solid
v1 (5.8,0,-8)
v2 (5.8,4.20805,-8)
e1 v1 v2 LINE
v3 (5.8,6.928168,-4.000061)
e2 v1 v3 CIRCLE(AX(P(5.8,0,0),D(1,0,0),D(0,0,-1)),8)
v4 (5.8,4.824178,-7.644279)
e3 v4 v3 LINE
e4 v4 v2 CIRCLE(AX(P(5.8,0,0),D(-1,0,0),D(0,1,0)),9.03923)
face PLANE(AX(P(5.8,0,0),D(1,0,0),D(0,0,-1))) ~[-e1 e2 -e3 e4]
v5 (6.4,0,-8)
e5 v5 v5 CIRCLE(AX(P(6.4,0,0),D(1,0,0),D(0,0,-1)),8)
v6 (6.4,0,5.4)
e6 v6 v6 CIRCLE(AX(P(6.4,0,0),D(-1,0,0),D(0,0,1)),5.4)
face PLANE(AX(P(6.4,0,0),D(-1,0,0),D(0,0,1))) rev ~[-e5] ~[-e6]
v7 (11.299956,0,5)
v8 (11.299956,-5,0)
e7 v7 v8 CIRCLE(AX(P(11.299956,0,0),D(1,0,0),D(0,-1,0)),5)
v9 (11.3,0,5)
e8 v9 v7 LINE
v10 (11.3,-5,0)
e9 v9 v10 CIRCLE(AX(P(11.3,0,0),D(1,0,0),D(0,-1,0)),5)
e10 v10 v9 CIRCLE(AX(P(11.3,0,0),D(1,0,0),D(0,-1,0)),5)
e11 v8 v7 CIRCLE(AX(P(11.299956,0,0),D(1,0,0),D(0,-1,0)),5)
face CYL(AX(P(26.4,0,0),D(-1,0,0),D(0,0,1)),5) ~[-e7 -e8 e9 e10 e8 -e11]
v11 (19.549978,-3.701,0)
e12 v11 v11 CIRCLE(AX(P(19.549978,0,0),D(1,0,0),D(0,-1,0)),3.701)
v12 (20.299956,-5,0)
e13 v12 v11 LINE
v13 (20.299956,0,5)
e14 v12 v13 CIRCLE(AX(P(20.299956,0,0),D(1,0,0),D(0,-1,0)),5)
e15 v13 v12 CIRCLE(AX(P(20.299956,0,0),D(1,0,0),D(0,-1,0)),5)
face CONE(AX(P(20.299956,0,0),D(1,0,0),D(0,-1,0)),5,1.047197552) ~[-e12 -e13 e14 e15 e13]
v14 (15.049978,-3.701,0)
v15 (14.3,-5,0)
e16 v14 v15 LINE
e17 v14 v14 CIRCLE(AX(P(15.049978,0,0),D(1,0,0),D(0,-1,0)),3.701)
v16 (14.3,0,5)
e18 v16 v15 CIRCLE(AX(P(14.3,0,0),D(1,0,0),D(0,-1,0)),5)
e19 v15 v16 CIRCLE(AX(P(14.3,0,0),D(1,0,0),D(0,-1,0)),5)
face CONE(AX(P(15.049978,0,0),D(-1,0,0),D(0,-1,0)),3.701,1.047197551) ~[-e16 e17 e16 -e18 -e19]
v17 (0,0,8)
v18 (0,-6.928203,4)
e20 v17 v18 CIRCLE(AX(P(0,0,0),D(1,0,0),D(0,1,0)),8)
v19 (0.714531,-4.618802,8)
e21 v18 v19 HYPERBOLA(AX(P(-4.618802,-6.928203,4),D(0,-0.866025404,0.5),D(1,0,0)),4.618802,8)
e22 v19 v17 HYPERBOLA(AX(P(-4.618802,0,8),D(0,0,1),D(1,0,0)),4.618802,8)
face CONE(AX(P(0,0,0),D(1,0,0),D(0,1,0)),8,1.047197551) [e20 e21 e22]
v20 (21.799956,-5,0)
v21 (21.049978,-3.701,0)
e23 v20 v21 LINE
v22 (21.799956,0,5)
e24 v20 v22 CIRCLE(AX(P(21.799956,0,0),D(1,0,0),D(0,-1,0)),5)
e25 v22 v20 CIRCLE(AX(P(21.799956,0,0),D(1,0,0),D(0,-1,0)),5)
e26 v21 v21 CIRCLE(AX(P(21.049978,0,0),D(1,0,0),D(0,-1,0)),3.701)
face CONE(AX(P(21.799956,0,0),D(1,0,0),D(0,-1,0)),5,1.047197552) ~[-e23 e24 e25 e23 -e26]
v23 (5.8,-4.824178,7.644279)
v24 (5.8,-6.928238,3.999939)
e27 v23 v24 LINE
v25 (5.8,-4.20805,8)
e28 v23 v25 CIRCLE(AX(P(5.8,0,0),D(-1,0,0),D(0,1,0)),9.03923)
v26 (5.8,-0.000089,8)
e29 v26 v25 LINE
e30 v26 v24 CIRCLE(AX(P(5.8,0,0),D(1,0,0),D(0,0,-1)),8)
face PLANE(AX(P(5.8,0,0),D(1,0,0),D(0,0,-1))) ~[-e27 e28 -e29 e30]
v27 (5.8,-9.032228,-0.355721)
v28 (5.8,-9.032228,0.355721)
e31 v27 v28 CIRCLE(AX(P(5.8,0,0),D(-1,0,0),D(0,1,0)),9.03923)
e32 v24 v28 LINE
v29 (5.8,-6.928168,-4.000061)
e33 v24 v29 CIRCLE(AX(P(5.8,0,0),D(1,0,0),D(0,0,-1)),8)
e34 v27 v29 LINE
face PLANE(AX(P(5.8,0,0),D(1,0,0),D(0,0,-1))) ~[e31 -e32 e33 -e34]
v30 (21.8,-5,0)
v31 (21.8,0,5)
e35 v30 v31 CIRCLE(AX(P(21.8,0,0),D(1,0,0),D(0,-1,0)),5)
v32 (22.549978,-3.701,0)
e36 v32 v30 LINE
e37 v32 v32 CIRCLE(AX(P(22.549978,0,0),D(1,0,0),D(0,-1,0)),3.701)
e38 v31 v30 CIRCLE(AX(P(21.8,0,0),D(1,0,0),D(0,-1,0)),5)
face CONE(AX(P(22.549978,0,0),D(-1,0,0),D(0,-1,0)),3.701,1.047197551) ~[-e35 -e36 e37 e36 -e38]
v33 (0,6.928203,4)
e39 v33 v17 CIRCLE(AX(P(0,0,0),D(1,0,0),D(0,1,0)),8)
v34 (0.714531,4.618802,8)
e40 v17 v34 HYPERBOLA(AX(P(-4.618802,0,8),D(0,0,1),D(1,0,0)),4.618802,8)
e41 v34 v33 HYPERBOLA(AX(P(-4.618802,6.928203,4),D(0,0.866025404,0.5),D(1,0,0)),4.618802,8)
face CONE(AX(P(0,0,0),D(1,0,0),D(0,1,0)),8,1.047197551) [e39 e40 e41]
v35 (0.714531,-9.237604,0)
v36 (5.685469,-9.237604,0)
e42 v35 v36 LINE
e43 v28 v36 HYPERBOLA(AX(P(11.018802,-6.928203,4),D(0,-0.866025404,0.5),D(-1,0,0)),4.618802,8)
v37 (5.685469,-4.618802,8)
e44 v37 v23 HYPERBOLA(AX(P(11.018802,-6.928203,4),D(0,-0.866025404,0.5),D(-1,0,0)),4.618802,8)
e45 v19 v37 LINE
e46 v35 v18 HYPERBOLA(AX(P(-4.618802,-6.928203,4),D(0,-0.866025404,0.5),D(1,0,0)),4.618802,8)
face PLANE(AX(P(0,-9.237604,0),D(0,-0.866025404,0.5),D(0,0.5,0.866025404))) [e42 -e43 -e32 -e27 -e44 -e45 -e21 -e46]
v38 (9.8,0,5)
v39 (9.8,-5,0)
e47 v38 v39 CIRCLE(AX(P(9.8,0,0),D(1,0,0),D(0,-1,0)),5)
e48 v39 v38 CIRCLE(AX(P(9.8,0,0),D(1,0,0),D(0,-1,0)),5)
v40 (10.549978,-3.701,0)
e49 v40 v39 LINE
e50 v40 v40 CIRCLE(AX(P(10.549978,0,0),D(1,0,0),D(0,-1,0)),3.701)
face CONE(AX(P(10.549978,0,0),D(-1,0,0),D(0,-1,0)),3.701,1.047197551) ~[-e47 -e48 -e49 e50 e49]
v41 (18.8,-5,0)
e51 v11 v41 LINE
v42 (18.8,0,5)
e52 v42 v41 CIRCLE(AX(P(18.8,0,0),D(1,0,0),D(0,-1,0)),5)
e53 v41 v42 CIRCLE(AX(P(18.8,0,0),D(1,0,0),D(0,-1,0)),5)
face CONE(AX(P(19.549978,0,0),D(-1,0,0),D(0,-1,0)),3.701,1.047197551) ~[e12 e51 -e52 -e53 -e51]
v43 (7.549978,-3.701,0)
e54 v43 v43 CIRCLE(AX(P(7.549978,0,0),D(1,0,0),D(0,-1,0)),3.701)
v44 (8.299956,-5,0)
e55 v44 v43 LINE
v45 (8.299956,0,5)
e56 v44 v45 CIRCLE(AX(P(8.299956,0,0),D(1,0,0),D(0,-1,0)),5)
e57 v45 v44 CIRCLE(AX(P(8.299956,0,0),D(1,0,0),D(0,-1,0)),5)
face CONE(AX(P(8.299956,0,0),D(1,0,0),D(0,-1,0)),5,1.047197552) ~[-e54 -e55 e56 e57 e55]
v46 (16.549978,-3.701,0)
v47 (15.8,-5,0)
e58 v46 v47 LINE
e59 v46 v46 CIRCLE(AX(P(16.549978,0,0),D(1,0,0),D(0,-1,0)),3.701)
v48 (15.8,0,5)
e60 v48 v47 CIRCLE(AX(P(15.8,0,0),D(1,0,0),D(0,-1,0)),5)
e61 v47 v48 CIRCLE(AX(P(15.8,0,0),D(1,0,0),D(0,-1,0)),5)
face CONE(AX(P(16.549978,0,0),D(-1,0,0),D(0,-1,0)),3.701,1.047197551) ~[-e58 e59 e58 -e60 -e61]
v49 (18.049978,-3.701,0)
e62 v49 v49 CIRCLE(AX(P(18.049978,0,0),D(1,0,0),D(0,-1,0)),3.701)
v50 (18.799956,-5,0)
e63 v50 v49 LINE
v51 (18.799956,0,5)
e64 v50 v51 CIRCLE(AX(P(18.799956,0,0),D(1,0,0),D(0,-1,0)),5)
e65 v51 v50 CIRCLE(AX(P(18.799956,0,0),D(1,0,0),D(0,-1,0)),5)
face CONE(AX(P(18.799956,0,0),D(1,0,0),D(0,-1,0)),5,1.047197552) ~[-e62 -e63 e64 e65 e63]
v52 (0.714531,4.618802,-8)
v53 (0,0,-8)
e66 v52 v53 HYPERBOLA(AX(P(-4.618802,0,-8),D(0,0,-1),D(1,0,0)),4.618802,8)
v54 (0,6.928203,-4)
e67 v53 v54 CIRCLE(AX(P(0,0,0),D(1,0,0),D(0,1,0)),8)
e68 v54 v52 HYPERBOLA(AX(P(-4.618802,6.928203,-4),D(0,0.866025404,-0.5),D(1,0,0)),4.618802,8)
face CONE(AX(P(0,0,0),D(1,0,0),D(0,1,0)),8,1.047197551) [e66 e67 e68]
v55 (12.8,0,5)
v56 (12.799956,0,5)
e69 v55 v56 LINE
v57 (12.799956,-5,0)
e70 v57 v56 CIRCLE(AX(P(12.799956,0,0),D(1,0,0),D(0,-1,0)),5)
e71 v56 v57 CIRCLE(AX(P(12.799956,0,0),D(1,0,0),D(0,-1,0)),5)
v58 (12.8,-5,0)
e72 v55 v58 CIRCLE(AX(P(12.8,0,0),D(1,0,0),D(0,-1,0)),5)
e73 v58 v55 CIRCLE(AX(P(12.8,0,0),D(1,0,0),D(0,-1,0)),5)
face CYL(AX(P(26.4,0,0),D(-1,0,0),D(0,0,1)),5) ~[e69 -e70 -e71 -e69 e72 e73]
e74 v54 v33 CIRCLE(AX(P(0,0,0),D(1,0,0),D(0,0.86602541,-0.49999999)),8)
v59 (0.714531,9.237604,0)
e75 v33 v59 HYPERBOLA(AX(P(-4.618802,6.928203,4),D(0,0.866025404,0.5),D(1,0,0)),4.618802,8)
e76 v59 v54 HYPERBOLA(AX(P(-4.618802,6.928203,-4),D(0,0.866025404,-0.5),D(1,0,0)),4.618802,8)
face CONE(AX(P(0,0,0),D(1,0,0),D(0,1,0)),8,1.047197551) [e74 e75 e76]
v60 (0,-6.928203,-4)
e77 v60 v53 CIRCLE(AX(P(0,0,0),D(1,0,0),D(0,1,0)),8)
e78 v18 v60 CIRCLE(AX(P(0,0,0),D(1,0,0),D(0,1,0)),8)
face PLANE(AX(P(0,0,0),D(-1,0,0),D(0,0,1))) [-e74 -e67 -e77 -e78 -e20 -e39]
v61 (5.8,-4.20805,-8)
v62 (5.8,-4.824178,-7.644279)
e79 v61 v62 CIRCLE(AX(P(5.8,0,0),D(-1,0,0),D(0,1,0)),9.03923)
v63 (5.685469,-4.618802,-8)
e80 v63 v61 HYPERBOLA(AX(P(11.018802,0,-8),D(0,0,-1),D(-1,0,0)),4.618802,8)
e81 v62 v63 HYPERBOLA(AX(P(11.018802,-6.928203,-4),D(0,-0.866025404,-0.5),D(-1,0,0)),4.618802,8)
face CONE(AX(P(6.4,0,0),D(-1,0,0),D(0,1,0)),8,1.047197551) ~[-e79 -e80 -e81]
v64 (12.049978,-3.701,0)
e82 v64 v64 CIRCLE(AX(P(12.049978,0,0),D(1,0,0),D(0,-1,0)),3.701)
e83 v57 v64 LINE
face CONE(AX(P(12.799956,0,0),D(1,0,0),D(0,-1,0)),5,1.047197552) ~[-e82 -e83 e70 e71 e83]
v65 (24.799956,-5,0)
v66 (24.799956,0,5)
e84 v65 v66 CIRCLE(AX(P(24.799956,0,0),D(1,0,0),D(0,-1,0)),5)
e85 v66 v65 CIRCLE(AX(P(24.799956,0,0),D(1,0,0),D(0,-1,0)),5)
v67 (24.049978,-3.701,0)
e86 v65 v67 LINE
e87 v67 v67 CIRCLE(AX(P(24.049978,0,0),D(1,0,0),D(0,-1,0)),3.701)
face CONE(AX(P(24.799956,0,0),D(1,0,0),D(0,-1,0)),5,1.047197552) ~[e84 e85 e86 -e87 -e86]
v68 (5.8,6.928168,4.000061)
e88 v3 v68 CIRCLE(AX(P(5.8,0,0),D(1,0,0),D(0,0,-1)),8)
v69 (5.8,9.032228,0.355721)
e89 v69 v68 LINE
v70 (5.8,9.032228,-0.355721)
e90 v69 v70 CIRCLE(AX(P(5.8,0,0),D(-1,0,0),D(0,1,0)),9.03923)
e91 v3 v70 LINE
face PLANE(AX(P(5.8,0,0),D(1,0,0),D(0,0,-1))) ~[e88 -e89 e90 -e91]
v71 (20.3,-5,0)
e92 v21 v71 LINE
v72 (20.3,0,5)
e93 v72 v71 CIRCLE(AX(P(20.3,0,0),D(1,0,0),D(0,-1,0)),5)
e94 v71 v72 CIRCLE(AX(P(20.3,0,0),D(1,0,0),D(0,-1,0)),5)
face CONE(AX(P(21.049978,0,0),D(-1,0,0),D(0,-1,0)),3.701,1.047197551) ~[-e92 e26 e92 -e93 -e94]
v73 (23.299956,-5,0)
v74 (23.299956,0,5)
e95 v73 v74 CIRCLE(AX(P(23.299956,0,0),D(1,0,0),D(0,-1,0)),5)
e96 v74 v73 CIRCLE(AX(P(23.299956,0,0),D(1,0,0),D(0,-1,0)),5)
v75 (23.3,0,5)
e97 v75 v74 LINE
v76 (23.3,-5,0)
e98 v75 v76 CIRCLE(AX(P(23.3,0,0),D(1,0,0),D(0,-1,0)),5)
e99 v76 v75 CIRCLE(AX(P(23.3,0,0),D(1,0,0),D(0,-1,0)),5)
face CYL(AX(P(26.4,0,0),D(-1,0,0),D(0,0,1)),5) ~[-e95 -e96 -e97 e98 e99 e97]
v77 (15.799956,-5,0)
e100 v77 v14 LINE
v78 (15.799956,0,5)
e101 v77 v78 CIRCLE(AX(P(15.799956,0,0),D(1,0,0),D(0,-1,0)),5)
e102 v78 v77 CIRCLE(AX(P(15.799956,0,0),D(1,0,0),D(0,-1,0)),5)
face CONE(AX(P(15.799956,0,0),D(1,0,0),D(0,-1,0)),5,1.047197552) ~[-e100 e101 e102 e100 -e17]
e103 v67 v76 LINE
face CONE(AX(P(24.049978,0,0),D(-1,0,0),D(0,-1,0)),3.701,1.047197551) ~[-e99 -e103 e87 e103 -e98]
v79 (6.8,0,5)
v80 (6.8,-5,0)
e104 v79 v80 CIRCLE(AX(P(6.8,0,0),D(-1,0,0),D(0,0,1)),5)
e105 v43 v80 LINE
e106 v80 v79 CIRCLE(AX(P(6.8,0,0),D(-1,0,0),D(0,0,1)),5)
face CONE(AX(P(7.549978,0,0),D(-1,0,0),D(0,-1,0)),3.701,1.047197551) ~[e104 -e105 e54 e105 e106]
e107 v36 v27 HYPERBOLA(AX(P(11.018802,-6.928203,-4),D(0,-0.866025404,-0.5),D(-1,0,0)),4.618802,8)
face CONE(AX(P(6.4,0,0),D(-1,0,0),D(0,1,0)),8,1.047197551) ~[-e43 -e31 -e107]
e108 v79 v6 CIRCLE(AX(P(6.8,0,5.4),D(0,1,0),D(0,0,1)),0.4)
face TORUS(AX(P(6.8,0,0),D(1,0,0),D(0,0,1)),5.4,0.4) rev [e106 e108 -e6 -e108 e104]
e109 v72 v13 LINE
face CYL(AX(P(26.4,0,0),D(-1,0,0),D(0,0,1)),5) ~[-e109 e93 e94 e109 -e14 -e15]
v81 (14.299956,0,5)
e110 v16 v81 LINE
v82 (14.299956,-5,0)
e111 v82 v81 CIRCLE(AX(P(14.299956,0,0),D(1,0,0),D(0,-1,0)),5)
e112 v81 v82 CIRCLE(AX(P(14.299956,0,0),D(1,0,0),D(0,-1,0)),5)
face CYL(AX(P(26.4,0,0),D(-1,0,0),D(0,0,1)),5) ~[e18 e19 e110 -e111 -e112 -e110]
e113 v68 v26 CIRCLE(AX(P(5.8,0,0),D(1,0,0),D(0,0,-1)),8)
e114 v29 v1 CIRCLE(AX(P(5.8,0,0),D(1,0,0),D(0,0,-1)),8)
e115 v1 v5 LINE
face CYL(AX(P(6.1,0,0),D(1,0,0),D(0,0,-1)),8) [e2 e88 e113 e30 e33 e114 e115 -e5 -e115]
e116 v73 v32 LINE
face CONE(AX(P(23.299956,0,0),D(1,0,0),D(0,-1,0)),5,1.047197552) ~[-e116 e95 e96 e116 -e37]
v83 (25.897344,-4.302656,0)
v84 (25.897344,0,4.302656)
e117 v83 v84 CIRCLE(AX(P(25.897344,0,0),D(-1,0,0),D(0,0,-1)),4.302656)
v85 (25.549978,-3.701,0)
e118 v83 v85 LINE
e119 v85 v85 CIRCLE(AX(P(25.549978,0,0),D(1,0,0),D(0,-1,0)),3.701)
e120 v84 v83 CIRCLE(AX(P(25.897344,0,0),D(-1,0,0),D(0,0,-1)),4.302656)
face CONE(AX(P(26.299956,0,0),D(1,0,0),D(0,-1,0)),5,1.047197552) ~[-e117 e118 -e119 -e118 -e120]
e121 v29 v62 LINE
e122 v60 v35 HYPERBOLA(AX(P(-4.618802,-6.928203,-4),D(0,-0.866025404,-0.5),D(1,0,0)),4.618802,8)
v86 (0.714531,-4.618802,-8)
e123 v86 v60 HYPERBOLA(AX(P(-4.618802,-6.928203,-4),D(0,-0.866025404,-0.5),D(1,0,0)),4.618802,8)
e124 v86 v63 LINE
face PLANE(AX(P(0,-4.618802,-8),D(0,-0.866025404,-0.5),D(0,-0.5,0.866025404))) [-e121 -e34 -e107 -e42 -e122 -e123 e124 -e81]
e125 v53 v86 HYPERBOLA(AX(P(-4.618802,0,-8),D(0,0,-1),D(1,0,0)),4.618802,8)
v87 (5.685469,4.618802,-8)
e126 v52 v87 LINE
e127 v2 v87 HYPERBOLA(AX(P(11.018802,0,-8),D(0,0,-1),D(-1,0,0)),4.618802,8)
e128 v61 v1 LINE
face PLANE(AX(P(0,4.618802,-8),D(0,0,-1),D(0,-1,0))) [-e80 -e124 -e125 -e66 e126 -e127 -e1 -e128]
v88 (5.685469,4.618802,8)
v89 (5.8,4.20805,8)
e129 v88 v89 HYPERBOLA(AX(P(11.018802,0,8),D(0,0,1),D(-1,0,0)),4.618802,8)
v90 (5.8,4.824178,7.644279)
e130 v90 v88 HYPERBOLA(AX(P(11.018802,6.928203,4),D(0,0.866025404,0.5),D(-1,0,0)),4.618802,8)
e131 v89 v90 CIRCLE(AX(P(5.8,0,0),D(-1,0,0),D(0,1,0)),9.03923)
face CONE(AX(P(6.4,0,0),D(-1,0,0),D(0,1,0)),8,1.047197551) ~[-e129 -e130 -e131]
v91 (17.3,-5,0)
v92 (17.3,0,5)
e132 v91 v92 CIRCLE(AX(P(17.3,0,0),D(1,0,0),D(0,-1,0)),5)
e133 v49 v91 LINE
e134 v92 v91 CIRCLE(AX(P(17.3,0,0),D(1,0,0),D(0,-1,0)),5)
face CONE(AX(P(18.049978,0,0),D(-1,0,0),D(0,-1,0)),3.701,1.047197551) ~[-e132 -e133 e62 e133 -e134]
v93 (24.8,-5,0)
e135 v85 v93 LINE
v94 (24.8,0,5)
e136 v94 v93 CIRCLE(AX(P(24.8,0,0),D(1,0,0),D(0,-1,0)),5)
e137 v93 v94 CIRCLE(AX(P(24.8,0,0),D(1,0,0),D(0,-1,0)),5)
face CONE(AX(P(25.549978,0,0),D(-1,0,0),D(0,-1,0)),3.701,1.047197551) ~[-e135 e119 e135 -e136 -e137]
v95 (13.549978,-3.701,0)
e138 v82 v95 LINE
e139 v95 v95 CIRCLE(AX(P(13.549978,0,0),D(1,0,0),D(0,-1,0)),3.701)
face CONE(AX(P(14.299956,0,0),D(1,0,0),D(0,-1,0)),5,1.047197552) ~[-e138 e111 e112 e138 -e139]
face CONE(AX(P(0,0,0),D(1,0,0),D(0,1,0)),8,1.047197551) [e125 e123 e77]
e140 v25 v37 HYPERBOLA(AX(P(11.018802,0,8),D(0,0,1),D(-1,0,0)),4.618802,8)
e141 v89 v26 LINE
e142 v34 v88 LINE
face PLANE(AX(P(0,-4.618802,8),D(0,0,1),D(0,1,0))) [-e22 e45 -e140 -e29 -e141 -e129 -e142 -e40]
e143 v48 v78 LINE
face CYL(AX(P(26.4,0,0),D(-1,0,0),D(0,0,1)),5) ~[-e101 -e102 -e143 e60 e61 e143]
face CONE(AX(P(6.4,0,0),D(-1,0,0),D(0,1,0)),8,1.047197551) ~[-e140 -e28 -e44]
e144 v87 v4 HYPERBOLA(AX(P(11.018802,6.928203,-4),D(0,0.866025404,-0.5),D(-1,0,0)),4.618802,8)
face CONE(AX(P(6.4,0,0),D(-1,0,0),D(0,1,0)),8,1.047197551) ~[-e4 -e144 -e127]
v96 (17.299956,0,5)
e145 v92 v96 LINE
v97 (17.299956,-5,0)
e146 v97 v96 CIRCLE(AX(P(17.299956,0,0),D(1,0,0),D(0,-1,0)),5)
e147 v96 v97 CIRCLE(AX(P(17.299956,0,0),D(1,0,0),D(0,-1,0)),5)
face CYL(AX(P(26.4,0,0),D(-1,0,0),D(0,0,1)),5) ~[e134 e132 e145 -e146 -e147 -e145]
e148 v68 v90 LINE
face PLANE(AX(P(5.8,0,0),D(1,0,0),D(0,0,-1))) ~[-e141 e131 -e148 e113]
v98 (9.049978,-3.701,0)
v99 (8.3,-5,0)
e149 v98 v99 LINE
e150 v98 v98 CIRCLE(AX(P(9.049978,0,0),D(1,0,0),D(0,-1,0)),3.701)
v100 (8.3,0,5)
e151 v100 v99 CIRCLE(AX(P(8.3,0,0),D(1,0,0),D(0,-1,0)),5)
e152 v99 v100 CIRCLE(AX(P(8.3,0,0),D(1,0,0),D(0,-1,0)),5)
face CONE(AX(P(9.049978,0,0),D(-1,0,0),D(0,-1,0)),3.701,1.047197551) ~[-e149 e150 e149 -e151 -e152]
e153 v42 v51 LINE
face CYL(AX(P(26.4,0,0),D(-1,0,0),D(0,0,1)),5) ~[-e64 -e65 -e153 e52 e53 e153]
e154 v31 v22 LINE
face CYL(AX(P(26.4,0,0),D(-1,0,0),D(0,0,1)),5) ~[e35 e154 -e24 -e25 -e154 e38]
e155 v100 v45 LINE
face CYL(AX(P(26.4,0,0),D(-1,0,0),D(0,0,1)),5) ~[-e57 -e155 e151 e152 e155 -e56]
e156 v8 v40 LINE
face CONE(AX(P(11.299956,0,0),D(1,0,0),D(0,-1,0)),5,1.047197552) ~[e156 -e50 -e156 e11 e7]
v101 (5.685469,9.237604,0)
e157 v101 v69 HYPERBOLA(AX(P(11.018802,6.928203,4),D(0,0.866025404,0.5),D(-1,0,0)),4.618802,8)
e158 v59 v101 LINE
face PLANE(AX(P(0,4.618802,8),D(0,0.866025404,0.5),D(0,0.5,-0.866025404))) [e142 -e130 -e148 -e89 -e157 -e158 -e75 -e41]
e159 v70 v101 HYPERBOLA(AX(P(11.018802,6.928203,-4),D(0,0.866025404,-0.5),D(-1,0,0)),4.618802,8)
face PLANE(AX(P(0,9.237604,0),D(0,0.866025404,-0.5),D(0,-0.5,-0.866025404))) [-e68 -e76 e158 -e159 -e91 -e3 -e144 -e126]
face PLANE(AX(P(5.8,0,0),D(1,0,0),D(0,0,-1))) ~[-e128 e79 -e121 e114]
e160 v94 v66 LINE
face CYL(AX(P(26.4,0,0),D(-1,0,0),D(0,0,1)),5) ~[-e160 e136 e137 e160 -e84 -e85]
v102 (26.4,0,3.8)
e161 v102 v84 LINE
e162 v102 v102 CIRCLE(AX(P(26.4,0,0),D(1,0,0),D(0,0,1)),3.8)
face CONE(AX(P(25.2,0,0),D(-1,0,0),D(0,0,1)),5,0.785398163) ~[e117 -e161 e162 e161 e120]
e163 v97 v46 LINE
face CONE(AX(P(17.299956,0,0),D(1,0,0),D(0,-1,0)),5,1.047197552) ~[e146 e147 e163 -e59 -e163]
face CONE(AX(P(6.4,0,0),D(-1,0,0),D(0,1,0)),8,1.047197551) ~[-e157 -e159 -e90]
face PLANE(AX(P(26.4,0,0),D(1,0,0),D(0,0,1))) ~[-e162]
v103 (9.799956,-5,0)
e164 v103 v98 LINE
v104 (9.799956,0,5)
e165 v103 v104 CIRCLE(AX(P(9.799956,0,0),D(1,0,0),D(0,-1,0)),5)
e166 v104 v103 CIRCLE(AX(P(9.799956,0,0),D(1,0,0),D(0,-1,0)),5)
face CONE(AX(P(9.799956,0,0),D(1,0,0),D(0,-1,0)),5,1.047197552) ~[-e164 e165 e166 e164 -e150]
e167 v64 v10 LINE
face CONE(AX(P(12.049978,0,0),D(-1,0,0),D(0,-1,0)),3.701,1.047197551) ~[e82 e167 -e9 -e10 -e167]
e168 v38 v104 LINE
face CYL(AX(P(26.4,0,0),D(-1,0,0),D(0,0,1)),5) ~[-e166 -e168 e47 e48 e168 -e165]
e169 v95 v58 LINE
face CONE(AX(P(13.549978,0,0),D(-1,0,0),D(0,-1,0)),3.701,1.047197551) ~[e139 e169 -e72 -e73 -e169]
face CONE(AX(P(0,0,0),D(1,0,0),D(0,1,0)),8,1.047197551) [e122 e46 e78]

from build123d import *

# Parameters (mm, degrees)
BOSS_EXTRUDE_DEPTH = 6.4
SKETCH4_W          = 0.6
SKETCH4_H          = 11.237604307
CHAMFER_2_SIZE     = 1.2
FILLET_2_R         = 0.4
LPATTERN1_COUNT    = 13
LPATTERN1_PITCH    = 1.5


with BuildPart() as part:
    # Sketch1 → Boss-Extrude (new body)
    with BuildSketch(Plane(origin=(0, 0, 0), x_dir=(0, 0, -1), z_dir=(1, 0, 0))):
        Polygon((8, 4.618802154), (8, -4.618802154), (0, -9.237604307), (-8, -4.618802154), (-8, 4.618802154), (0, 9.237604307), align=None)
    extrude(amount=BOSS_EXTRUDE_DEPTH)

    # Sketch2 → Boss-Revolve1 (revolve)
    with BuildSketch(Plane.XY, mode=Mode.PRIVATE) as boss_revolve1_sk:
        Polygon((0, 0), (26.4, 0), (26.4, 3.701), (26.4, 5), (0, 5), align=None)
    revolve(boss_revolve1_sk.sketch.rotate(Axis((0, 0, 0), (1, 0, 0)), 90), axis=Axis((0, 0, 0), (1, 0, 0)))

    # Sketch3 → Cut-Revolve1 (revolve, cut)
    with BuildSketch(Plane.XY):
        Polygon((0, 8), (3.601282526, 14.237604307), (3.601282526, 19.237604307), (-10, 19.237604307), (-10, 8), align=None)
    revolve(axis=Axis((0, 0, 0), (1, 0, 0)), mode=Mode.SUBTRACT)

    # Sketch5 → Cut-Revolve2 (revolve, cut)
    with BuildSketch(Plane.XY):
        Polygon((6.4, 8), (2.798717474, 14.237604307), (2.798717474, 19.237604307), (12.798717474, 19.237604307), (12.798717474, 8), align=None)
    revolve(axis=Axis((0, 0, 0), (1, 0, 0)), mode=Mode.SUBTRACT)

    # Sketch4 → Cut-Revolve3 (revolve, cut)
    with BuildSketch(Plane.XY, mode=Mode.PRIVATE) as cut_revolve3_sk:
        with Locations((6.1, 13.618802154)):
            Rectangle(SKETCH4_W, SKETCH4_H)
    revolve(cut_revolve3_sk.sketch.rotate(Axis((0, 0, 0), (1, 0, 0)), 270), axis=Axis((0, 0, 0), (1, 0, 0)), mode=Mode.SUBTRACT)

    # Chamfer 2
    chamfer_2_edges = [part.edges().sort_by_distance(p)[0] for p in [
        (26.4, 0, -5),
    ]]
    chamfer(chamfer_2_edges, length=CHAMFER_2_SIZE)

    # Fillet 2
    fillet_2_edges = [part.edges().sort_by_distance(p)[0] for p in [
        (6.4, 0, -5),
    ]]
    fillet(fillet_2_edges, radius=FILLET_2_R)

    # Sketch6 → Cut-Revolve4 (revolve, cut)
    with BuildSketch(Plane.XY):
        Polygon((7.549978, -3.701), (6.8, -5), (6.8, -6.25), (8.299955999, -6.25), (8.299955999, -5), align=None)
    cut_revolve4 = revolve(axis=Axis((-3.175, 0, 0), (1, 0, 0)), mode=Mode.SUBTRACT)

    # LPattern1: Cut-Revolve4 ×13
    with Locations(*[(i * LPATTERN1_PITCH, 0, 0) for i in range(1, LPATTERN1_COUNT)]):
        add(cut_revolve4, mode=Mode.SUBTRACT)


solid = part.part
